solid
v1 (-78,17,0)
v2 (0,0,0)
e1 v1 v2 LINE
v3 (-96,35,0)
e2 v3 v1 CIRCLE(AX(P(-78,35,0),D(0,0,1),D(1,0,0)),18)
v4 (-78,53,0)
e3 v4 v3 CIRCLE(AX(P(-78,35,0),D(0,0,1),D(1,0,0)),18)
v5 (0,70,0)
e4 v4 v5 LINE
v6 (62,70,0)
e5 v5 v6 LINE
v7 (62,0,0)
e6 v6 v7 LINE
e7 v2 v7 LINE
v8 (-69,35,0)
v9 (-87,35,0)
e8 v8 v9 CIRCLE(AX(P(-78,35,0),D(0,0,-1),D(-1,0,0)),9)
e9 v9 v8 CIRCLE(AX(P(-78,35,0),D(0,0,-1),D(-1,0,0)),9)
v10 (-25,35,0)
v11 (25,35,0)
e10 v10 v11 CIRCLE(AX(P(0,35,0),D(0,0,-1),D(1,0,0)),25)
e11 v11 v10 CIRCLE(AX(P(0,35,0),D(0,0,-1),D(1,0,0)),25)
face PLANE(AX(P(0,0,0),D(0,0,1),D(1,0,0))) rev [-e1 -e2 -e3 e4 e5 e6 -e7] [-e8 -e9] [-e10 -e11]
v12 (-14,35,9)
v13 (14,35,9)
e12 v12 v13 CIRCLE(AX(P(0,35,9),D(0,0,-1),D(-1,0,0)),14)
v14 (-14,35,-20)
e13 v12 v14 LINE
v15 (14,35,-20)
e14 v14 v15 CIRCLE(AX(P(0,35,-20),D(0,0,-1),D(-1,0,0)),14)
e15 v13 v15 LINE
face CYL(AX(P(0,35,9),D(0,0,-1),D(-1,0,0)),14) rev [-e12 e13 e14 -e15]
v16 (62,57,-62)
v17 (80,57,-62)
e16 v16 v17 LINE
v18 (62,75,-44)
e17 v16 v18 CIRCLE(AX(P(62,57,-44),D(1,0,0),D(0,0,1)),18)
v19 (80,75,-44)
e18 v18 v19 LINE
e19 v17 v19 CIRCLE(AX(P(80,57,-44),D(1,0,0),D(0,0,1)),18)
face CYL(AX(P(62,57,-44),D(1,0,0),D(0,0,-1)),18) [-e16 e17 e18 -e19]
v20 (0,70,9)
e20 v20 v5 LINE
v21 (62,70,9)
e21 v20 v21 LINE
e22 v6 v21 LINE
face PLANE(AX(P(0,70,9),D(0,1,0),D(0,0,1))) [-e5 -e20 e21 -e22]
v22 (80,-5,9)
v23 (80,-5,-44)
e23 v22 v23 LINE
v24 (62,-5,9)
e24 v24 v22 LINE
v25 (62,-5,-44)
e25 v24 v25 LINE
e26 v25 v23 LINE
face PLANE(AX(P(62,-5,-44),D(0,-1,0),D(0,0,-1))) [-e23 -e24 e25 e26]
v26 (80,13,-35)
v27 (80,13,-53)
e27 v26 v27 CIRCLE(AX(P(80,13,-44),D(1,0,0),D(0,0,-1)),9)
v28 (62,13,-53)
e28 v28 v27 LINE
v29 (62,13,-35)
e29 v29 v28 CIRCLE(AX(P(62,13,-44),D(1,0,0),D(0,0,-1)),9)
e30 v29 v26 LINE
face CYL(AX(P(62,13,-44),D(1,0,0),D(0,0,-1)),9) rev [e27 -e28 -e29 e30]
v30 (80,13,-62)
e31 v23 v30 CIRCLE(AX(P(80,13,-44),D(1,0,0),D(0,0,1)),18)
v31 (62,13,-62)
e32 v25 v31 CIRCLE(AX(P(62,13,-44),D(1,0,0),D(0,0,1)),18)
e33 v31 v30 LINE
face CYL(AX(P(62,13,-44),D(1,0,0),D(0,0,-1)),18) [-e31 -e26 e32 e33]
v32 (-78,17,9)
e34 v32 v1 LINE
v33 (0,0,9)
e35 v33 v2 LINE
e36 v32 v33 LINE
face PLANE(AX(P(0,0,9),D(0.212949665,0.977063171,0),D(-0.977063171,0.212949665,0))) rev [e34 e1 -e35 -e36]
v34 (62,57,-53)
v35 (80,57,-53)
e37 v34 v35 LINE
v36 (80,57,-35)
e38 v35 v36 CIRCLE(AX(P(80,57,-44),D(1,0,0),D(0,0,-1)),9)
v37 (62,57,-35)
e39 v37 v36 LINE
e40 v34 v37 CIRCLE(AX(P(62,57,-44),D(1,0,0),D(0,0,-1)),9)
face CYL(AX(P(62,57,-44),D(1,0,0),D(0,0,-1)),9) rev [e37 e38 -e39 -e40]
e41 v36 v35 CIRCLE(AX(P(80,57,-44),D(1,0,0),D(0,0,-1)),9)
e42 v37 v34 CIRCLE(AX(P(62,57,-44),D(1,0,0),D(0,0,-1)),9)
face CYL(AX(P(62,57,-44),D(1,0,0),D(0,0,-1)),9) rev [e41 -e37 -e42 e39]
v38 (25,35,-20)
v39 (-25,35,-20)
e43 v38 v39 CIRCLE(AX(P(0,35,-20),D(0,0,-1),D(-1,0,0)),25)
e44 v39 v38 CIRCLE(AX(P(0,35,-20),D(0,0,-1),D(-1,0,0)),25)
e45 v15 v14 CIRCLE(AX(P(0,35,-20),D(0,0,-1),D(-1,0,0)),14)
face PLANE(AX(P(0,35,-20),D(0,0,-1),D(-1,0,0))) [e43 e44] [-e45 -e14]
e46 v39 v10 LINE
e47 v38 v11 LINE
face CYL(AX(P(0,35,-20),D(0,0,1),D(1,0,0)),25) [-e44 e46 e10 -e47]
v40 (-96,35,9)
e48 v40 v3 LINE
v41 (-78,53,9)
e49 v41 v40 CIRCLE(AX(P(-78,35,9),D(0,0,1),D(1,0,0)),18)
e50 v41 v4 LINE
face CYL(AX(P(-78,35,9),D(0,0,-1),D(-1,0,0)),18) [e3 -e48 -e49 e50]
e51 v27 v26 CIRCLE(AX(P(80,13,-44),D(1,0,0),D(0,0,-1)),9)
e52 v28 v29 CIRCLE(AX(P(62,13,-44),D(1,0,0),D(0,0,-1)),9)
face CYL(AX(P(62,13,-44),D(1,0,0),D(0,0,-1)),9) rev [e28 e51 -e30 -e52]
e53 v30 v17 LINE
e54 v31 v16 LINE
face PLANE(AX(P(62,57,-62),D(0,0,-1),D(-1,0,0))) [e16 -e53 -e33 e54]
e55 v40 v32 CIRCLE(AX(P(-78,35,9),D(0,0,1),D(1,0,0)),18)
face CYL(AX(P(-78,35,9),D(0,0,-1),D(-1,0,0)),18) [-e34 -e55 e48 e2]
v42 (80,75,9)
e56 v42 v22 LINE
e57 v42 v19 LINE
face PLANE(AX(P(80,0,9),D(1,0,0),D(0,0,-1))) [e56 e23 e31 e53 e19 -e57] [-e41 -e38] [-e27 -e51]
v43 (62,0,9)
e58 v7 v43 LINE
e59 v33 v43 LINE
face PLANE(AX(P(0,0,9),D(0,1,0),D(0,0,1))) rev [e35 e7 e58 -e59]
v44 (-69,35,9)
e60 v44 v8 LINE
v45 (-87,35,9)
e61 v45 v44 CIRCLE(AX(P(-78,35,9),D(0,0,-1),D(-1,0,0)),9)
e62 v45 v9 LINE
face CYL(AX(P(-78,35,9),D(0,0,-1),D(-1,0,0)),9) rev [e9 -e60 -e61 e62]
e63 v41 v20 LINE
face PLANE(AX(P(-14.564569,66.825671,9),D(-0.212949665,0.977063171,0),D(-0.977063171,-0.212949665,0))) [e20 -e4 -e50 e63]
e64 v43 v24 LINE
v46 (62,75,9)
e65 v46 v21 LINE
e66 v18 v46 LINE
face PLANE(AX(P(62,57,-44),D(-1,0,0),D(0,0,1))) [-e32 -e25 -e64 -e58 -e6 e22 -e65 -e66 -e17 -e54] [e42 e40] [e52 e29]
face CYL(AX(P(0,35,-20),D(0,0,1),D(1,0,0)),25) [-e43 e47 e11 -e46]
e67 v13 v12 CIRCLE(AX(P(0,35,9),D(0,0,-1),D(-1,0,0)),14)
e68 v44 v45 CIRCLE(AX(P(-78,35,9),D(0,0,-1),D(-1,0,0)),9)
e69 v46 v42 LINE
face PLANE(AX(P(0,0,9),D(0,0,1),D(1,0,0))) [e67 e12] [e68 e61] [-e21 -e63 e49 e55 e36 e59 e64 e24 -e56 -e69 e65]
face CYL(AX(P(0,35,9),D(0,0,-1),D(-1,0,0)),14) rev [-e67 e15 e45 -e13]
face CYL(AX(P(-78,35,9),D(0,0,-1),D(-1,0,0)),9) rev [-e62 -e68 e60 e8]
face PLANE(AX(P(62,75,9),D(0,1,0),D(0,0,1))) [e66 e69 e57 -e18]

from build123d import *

# Parameters (mm, degrees)
BASE_PLATE_DEPTH              = 9
END_HOLE_18_SKETCH_R          = 9
END_HOLE_18_DEPTH             = 9
PIVOT_BOSS_50_SKETCH_R        = 25
PIVOT_BOSS_50_DEPTH           = 20
PIVOT_BORE_28_SKETCH_R        = 14
PIVOT_BORE_28_DEPTH           = 126.227792442
MOUNTING_BLOCK_DEPTH          = 18
MOUNTING_HOLES_2X_18_SKETCH_R = 9
MOUNTING_HOLES_2X_18_DEPTH    = 18


with BuildPart() as part:
    # Base Plate Profile Sketch → Base Plate (new body)
    with BuildSketch(Plane.XY):
        with BuildLine():
            Line((-78, 53), (0, 70))
            Line((0, 70), (69.753049234, 70))
            ThreePointArc((69.753049234, 70), (75.45392636, 71.316678554), (80, 75))
            Line((80, 75), (80, -5))
            ThreePointArc((80, -5), (75.45392636, -1.316678554), (69.753049234, 0))
            Line((69.753049234, 0), (0, 0))
            Line((0, 0), (-78, 17))
            ThreePointArc((-78, 17), (-96, 35), (-78, 53))
        make_face()
    extrude(amount=BASE_PLATE_DEPTH)

    # End Hole Ø18 Sketch → End Hole Ø18 (cut)
    with BuildSketch(Plane(origin=(0, 0, 0), x_dir=(-1, 0, 0), z_dir=(0, 0, -1))):
        with Locations((78, 35)):
            Circle(END_HOLE_18_SKETCH_R)
    extrude(amount=-END_HOLE_18_DEPTH, mode=Mode.SUBTRACT)

    # Pivot Boss Ø50 Sketch → Pivot Boss Ø50 (add)
    with BuildSketch(Plane(origin=(0, 0, 0), x_dir=(-1, 0, 0), z_dir=(0, 0, -1))):
        with Locations(Location((0, 35, 0), (0, 0, 180))):
            Circle(PIVOT_BOSS_50_SKETCH_R)
    extrude(amount=PIVOT_BOSS_50_DEPTH)

    # Pivot Bore Ø28 Sketch → Pivot Bore Ø28 (cut, through all)
    with BuildSketch(Plane(origin=(0, 0, -20), x_dir=(-1, 0, 0), z_dir=(0, 0, -1))):
        with Locations((0, 35)):
            Circle(PIVOT_BORE_28_SKETCH_R)
    extrude(amount=-PIVOT_BORE_28_DEPTH, mode=Mode.SUBTRACT)

    # Mounting Block Sketch → Mounting Block (add)
    with BuildSketch(Plane(origin=(80, 0, 0), x_dir=(0, 0, -1), z_dir=(1, 0, 0))):
        with BuildLine():
            Line((-9, 75), (44, 75))
            ThreePointArc((44, 75), (56.727922061, 69.727922061), (62, 57))
            Line((62, 57), (62, 13))
            ThreePointArc((62, 13), (56.727922061, 0.272077939), (44, -5))
            Line((44, -5), (-9, -5))
            Line((-9, -5), (-9, 75))
        make_face()
    extrude(amount=-MOUNTING_BLOCK_DEPTH)

    # Mounting Holes 2xØ18 Sketch → Mounting Holes 2xØ18 (cut)
    with BuildSketch(Plane(origin=(80, 0, 0), x_dir=(0, 0, -1), z_dir=(1, 0, 0))):
        with Locations((44, 57)):
            Circle(MOUNTING_HOLES_2X_18_SKETCH_R)
        with Locations((44, 13)):
            Circle(MOUNTING_HOLES_2X_18_SKETCH_R)
    extrude(amount=-MOUNTING_HOLES_2X_18_DEPTH, mode=Mode.SUBTRACT)


solid = part.part
